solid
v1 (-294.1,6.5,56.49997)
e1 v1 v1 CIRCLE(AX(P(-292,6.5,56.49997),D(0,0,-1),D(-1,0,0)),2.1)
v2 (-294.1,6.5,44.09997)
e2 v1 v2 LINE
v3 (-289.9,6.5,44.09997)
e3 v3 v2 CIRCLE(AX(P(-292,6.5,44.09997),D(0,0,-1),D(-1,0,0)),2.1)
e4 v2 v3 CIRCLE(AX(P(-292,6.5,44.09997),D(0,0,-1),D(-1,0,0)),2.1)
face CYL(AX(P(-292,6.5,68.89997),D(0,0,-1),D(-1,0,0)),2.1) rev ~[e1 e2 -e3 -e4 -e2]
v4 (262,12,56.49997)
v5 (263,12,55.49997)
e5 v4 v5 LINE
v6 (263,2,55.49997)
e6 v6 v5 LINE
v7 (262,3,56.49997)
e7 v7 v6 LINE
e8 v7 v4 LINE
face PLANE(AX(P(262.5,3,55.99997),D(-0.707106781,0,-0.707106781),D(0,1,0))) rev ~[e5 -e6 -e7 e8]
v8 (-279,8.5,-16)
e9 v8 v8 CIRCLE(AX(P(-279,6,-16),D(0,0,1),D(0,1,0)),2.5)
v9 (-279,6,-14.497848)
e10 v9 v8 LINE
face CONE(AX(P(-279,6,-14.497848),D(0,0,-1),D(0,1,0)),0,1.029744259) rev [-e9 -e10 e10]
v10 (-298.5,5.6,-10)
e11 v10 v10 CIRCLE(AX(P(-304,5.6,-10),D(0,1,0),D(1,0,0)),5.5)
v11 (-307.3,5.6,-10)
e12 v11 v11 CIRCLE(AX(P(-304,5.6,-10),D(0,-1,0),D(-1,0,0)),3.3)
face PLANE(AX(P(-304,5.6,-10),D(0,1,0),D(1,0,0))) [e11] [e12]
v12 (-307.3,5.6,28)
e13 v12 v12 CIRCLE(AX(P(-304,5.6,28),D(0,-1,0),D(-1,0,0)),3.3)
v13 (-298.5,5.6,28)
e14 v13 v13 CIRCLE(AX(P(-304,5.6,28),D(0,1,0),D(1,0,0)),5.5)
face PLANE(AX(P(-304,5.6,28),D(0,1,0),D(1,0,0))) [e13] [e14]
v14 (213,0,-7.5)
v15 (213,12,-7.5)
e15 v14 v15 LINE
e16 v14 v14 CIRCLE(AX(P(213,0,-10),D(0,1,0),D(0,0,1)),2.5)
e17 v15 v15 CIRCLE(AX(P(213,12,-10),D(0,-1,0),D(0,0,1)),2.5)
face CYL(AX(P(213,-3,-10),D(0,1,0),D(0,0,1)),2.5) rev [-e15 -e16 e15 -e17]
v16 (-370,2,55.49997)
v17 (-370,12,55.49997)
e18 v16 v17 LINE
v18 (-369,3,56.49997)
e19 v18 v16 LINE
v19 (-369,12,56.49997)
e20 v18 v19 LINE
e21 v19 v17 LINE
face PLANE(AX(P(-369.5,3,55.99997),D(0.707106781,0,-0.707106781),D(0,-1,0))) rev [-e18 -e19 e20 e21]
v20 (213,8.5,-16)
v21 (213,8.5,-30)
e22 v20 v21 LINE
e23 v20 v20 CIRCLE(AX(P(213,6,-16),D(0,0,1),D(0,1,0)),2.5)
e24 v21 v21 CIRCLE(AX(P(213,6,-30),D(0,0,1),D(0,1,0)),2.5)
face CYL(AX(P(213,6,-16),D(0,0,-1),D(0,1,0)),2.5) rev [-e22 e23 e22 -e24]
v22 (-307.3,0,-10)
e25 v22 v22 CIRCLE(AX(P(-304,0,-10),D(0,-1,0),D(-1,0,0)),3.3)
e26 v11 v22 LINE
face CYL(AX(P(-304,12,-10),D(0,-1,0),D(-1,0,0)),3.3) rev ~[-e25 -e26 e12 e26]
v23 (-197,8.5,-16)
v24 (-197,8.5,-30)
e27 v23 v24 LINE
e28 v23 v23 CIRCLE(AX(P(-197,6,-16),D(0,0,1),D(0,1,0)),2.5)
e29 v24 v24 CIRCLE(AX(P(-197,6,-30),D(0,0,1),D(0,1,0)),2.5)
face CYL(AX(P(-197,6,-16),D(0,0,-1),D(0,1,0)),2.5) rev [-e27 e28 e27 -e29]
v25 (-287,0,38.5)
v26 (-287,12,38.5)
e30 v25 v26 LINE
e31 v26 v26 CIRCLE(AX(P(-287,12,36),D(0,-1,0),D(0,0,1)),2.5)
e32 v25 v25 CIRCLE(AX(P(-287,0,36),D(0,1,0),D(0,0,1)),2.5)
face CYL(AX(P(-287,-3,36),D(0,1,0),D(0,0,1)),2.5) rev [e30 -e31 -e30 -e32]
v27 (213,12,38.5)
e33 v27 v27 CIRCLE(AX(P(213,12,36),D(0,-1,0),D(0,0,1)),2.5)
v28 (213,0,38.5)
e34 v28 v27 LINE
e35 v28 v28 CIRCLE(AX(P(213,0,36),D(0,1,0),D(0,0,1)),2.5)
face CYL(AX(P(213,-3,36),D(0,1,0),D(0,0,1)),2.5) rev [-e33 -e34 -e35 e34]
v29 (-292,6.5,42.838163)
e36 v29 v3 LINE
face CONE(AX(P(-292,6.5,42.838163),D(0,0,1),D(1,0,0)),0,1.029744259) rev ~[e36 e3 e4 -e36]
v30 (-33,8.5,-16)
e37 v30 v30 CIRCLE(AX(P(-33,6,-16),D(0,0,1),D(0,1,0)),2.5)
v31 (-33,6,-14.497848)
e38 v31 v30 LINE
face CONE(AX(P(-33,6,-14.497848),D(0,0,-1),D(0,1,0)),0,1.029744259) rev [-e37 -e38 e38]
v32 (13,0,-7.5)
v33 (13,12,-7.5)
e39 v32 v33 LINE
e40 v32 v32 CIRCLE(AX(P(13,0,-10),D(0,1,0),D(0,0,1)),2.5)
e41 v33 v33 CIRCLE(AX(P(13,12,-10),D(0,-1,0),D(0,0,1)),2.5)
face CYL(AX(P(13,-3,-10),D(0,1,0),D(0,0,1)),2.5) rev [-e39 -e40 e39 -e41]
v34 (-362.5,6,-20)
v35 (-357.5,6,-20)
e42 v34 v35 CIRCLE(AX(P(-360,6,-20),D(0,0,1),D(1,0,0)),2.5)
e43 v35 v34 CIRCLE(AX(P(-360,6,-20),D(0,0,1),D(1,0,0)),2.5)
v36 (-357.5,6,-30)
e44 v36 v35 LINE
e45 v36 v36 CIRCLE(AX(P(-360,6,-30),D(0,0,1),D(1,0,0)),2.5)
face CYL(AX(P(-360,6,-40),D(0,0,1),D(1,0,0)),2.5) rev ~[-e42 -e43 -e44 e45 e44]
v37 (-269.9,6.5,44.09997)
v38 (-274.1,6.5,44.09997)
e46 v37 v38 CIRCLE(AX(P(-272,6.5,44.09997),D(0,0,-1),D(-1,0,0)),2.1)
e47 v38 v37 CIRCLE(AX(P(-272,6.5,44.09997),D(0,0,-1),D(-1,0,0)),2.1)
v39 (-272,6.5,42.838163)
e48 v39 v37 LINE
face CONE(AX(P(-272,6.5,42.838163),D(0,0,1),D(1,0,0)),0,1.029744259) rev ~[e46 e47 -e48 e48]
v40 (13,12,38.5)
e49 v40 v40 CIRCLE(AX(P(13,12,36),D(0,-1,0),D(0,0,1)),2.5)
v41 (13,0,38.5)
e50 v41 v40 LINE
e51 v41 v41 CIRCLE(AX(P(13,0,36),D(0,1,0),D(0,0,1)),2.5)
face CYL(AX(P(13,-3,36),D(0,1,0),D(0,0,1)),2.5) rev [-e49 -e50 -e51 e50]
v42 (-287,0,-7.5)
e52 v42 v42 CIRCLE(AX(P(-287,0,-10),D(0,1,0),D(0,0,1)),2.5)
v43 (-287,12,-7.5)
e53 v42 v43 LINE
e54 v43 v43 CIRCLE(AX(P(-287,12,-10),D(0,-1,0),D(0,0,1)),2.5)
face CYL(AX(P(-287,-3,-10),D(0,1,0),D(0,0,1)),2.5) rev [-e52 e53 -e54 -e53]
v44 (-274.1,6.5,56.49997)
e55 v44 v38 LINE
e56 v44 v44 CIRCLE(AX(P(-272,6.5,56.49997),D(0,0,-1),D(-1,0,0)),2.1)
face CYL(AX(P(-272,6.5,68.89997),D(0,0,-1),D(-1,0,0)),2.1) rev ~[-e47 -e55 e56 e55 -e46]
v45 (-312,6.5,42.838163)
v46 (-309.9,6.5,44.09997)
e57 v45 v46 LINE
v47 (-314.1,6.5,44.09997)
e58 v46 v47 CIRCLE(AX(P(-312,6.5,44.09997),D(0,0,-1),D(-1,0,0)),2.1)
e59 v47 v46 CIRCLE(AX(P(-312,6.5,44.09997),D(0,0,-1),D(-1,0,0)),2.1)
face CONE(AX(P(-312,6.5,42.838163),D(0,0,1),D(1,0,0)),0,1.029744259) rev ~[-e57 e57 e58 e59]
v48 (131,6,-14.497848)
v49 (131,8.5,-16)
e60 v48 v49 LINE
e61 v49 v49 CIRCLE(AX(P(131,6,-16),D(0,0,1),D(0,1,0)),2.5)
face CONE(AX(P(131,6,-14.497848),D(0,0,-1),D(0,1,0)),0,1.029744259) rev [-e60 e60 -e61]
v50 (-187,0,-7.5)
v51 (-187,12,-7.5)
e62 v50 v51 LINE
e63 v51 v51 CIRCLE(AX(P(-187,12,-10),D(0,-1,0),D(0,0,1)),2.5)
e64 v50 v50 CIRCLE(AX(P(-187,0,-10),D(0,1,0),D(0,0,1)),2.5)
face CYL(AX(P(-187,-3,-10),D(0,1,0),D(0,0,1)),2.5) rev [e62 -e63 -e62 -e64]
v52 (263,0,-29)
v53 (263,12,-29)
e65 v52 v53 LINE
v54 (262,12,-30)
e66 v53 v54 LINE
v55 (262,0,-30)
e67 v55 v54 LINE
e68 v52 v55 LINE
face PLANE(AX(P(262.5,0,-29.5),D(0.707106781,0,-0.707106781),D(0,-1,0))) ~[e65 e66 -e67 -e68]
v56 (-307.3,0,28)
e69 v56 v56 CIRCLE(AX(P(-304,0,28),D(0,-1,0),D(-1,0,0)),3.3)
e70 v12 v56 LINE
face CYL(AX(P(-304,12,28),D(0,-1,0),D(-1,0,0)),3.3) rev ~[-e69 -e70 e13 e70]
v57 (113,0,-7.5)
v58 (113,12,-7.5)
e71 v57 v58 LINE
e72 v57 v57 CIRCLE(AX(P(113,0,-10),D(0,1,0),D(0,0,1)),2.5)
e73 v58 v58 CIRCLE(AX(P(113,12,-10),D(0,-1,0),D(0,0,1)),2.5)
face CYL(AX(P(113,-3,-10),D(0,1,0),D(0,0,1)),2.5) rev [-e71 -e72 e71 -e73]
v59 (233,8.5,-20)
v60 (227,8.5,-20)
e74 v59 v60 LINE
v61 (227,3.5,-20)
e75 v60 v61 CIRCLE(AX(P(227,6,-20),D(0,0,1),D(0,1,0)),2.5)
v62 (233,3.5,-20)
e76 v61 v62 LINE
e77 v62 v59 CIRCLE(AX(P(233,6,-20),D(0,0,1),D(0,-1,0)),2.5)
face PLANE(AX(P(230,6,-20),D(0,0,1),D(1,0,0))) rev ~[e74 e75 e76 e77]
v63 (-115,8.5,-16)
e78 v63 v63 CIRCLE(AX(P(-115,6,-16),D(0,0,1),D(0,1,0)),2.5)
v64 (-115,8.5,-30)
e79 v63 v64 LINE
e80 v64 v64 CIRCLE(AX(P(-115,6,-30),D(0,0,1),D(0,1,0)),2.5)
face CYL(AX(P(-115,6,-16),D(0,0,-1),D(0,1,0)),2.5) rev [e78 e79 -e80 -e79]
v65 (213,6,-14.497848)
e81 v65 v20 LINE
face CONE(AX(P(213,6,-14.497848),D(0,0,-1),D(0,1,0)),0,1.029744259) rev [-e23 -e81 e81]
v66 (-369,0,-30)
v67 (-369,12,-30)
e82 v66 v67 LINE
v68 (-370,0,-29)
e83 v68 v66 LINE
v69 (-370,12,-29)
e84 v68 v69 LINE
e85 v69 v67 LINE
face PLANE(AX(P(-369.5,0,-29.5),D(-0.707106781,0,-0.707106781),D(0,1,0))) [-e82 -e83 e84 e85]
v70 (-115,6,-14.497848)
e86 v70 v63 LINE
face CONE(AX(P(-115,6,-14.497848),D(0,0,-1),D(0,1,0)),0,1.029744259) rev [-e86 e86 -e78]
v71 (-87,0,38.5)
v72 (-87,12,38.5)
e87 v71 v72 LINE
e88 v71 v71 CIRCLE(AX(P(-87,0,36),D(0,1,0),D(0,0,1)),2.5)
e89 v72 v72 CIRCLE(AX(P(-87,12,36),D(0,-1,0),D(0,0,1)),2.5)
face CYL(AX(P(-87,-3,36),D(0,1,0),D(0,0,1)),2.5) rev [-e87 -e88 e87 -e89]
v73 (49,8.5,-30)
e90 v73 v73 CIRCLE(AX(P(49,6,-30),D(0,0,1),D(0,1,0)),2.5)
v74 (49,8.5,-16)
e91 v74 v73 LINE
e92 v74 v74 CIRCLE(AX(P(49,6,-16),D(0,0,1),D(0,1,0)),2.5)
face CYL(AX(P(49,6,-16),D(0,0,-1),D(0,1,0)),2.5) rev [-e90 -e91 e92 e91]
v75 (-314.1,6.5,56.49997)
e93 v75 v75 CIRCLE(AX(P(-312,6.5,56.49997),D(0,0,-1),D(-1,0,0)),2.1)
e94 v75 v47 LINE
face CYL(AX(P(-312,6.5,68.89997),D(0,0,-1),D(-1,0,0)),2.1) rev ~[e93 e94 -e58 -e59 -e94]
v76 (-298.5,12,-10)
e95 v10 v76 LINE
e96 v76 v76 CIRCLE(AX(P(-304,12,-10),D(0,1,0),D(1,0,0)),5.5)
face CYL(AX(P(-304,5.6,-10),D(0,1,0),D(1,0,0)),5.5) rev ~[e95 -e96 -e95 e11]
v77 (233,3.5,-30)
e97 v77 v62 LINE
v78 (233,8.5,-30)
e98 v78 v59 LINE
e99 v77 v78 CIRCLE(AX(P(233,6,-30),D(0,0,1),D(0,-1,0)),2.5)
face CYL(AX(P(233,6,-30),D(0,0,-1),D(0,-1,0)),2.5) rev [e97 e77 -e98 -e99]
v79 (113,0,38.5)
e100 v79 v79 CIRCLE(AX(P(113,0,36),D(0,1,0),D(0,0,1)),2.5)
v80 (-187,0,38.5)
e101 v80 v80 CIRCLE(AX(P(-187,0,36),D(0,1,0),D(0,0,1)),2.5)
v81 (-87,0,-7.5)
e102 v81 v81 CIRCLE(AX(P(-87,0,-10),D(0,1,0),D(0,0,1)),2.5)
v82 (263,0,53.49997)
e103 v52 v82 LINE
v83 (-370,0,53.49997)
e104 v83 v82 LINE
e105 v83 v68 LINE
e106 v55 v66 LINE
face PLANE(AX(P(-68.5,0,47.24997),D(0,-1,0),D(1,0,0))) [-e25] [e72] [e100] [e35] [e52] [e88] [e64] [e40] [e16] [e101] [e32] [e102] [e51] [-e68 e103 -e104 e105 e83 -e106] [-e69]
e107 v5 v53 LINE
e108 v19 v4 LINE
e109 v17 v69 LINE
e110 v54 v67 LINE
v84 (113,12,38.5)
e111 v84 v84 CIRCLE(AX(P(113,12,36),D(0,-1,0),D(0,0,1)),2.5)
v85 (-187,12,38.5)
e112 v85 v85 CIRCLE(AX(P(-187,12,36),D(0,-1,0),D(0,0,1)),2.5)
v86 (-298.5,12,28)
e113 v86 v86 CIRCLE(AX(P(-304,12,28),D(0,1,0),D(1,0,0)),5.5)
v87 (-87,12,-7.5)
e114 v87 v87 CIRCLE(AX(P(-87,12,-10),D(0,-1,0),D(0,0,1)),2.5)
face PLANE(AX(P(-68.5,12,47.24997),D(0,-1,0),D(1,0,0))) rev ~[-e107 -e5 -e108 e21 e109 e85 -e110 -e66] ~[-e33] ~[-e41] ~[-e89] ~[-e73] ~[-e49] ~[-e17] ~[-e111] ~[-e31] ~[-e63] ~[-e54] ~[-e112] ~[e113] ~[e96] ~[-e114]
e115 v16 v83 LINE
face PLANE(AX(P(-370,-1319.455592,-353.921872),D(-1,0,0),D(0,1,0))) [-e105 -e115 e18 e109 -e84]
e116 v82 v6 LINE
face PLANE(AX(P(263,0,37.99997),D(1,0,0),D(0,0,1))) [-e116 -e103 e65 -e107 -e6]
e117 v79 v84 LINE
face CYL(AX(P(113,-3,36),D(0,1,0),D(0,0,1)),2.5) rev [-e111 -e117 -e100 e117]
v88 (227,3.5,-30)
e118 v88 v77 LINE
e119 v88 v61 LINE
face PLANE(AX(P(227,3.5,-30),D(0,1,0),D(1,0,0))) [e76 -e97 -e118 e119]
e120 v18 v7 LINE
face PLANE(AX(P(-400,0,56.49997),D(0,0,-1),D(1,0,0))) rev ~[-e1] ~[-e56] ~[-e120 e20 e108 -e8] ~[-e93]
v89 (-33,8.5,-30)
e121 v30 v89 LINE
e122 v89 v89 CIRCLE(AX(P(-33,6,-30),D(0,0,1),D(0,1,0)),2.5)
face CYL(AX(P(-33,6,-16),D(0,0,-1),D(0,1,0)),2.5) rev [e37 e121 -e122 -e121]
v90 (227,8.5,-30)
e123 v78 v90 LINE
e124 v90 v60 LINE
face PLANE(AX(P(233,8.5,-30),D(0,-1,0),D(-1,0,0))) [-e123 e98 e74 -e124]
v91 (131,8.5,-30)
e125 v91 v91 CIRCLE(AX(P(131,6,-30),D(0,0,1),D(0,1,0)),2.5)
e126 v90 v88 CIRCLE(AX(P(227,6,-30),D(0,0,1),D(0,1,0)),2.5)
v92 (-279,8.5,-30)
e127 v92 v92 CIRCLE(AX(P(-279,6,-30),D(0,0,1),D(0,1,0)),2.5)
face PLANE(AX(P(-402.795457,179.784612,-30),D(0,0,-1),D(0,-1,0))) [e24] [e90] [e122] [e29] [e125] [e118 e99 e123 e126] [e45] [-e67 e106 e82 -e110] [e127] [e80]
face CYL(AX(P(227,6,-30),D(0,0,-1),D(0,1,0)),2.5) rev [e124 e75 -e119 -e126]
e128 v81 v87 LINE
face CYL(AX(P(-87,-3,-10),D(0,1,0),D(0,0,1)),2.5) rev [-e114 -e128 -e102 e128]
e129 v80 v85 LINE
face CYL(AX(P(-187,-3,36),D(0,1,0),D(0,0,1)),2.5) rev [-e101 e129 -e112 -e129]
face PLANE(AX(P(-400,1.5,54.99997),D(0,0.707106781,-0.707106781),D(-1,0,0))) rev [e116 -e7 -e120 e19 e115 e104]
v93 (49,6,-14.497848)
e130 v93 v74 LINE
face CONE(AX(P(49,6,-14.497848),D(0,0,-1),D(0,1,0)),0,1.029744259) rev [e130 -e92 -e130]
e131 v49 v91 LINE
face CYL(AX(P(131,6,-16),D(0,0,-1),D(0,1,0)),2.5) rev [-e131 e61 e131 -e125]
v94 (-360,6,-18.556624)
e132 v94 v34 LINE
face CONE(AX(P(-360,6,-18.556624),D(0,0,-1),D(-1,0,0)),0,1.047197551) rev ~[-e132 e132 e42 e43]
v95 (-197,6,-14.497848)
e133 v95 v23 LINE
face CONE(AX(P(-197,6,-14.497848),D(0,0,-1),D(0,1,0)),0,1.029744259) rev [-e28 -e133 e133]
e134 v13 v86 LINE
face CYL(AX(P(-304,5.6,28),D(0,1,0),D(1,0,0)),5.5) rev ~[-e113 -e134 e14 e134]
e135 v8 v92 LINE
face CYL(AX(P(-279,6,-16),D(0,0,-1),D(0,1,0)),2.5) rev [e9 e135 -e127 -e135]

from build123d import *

# Parameters (mm, degrees)
SKETCH_1_W                     = 800
SKETCH_1_H                     = 80
EXTRUDE_1_DEPTH                = 12
SKETCH_13_W                    = 10
SKETCH_13_H                    = 40
EXTRUDE_2_DEPTH                = 800
CUT_EXTRUDE_1_DEPTH            = 409.881400898
CUT_EXTRUDE_1_DEPTH_BACK       = 409.881400898
SKETCH_15_W                    = 47
SKETCH_15_H                    = 70
CUT_EXTRUDE_2_DEPTH            = 403.968981437
CUT_EXTRUDE_3_DEPTH            = 665.795457265
CUT_EXTRUDE_3_DEPTH_BACK       = 665.795457265
CUT_EXTRUDE_4_DEPTH            = 665.795457265
CUT_EXTRUDE_4_DEPTH_BACK       = 665.795457265
PATTERN_LINEAR_1_COUNT         = 7
PATTERN_LINEAR_1_PITCH         = 82
HOLE_WIZARD_M6_1_2_D           = 6.6
HOLE_WIZARD_M6_1_2_CBORE_D     = 11
HOLE_WIZARD_M6_1_2_CBORE_DEPTH = 6.4
HOLE_WIZARD_5_0_5_1_D          = 5
HOLE_WIZARD_5_0_5_1_DEPTH      = 10
HOLE_WIZARD_5_0_5_1_TIP        = 1.443375673
CUT_EXTRUDE_5_DEPTH            = 10
SKETCH_26_W                    = 663
SKETCH_26_H                    = 18.5
EXTRUDE_3_DEPTH                = 12
CHAMFER_1_SIZE                 = 3
HOLE_WIZARD_M6_2_AT_2_COUNT    = 2
HOLE_WIZARD_M6_2_AT_2_PITCH    = 46
PATTERN_LINEAR_2_COUNT         = 6
PATTERN_LINEAR_2_PITCH         = 100
HOLE_WIZARD_M5_1_D             = 4.2
HOLE_WIZARD_M5_1_DEPTH         = 12.4
HOLE_WIZARD_M5_1_TIP           = 1.2618073
CUT_EXTRUDE_6_DEPTH            = 410.421842126
CUT_EXTRUDE_6_DEPTH_BACK       = 410.421842126
CHAMFER_2_SIZE                 = 1


with BuildPart() as part:
    # 草图1 → 凸台-拉伸1 (new body)
    with BuildSketch(Plane(origin=(0, 0, 0), x_dir=(1, 0, 0), z_dir=(0, 1, 0))):
        Rectangle(SKETCH_1_W, SKETCH_1_H)
    extrude(amount=EXTRUDE_1_DEPTH)

    # 草图13 → 凸台-拉伸2 (add)
    with BuildSketch(Plane(origin=(400, 0, 0), x_dir=(0, 0, -1), z_dir=(1, 0, 0))):
        with Locations((35, -8)):
            Rectangle(SKETCH_13_W, SKETCH_13_H)
    extrude(amount=-EXTRUDE_2_DEPTH)

    # 草图14 → 切除-拉伸1 (cut, two sides: drawn at the far end of the back side and taken through both)
    with BuildSketch(Plane.XY.offset(40).offset(-CUT_EXTRUDE_1_DEPTH_BACK)):
        Polygon((310, 1445.673153531), (310, 12), (310, -39.100998243), (310, -1472.774151774), (3177.346307063, -1472.774151774), (3177.346307063, 1445.673153531), align=None)
    extrude(amount=CUT_EXTRUDE_1_DEPTH + CUT_EXTRUDE_1_DEPTH_BACK, mode=Mode.SUBTRACT)

    # 草图15 → 切除-拉伸2 (cut, through all)
    with BuildSketch(Plane.XZ):
        with Locations((286.5, 5)):
            Rectangle(SKETCH_15_W, SKETCH_15_H)
    extrude(amount=-CUT_EXTRUDE_2_DEPTH, mode=Mode.SUBTRACT)

    # 草图16 → 切除-拉伸3 (cut, two sides: drawn at the far end of the back side and taken through both)
    with BuildSketch(Plane(origin=(263, 0, 0), x_dir=(0, 0, -1), z_dir=(1, 0, 0)).offset(-CUT_EXTRUDE_3_DEPTH_BACK)):
        Polygon((-37.99997, 201.49334526), (-37.99997, 14.161837787), (-37.99997, -5.873299283), (-37.99997, -193.204806756), (-412.662984945, -193.204806756), (-412.662984945, 201.49334526), align=None)
    extrude(amount=CUT_EXTRUDE_3_DEPTH + CUT_EXTRUDE_3_DEPTH_BACK, mode=Mode.SUBTRACT)

    # 草图17 → 切除-拉伸4 (cut, two sides: drawn at the far end of the back side and taken through both)
    with BuildSketch(Plane(origin=(263, 0, 0), x_dir=(0, 0, -1), z_dir=(1, 0, 0)).offset(-CUT_EXTRUDE_4_DEPTH_BACK)):
        Polygon((30, 179.784611671), (30, 12), (30, -28), (30, -195.784611671), (365.569223341, -195.784611671), (365.569223341, 179.784611671), align=None)
    extrude(amount=CUT_EXTRUDE_4_DEPTH + CUT_EXTRUDE_4_DEPTH_BACK, mode=Mode.SUBTRACT)

    # 草图18 → Hole Wizard M6 _1 (revolve, cut)
    with BuildSketch(Plane(origin=(213, 6, -30), x_dir=(0, 1, 0), z_dir=(1, 0, 0))):
        Polygon((0, 0), (0, 15.502151548), (2.5, 14), (2.5, 0), align=None)
    hole_wizard_m6_1 = revolve(axis=Axis((213, 6, -36.35), (0, 0, 1)), mode=Mode.SUBTRACT)

    # 阵列(线性)1: Hole Wizard M6 _1 ×7
    with Locations(*[(-i * PATTERN_LINEAR_1_PITCH, 0, 0) for i in range(1, PATTERN_LINEAR_1_COUNT)]):
        add(hole_wizard_m6_1, mode=Mode.SUBTRACT)

    # Hole Wizard M6 _1 2 (through all)
    with Locations(Plane(origin=(0, 12, 0), x_dir=(1, 0, 0), z_dir=(0, 1, 0))):
        with Locations((-304, 10), (-304, -28)):
            CounterBoreHole(HOLE_WIZARD_M6_1_2_D / 2, HOLE_WIZARD_M6_1_2_CBORE_D / 2, HOLE_WIZARD_M6_1_2_CBORE_DEPTH)

    # Ø5.0 (5) 直径孔1
    with Locations(Plane(origin=(0, 0, -30), x_dir=(-1, 0, 0), z_dir=(0, 0, -1))):
        with Locations((360, 6)):
            Hole(HOLE_WIZARD_5_0_5_1_D / 2, depth=HOLE_WIZARD_5_0_5_1_DEPTH)
            with Locations((0, 0, -(HOLE_WIZARD_5_0_5_1_DEPTH + HOLE_WIZARD_5_0_5_1_TIP / 2))):  # 120° drill point
                Cone(0, HOLE_WIZARD_5_0_5_1_D / 2, HOLE_WIZARD_5_0_5_1_TIP, mode=Mode.SUBTRACT)

    # 草图24 → 切除-拉伸5 (cut)
    with BuildSketch(Plane(origin=(0, 0, -30), x_dir=(-1, 0, 0), z_dir=(0, 0, -1))):
        with BuildLine():
            Line((-227, 3.5), (-233, 3.5))
            ThreePointArc((-233, 3.5), (-235.5, 6), (-233, 8.5))
            Line((-233, 8.5), (-227, 8.5))
            ThreePointArc((-227, 8.5), (-224.5, 6), (-227, 3.5))
        make_face()
    extrude(amount=-CUT_EXTRUDE_5_DEPTH, mode=Mode.SUBTRACT)

    # 草图26 → 凸台-拉伸3 (add)
    with BuildSketch(Plane.XZ):
        with Locations((-68.5, 47.24997)):
            Rectangle(SKETCH_26_W, SKETCH_26_H)
    extrude(amount=-EXTRUDE_3_DEPTH)

    # 倒角1
    chamfer_1_edges = [part.edges().sort_by_distance(p)[0] for p in [
        (-68.5, 0, 56.49997),
    ]]
    chamfer(chamfer_1_edges, length=CHAMFER_1_SIZE)

    # 草图27 → M6 螺纹孔2 (revolve, cut)
    with BuildSketch(Plane(origin=(213, 12, -10), x_dir=(0, 0, 1), z_dir=(1, 0, 0))):
        Polygon((0, 0), (0, 16.502151548), (2.5, 15), (2.5, 0), align=None)
    hole_wizard_m6_2 = revolve(axis=Axis((213, 18.35, -10), (0, -1, 0)), mode=Mode.SUBTRACT)

    # M6 螺纹孔2 at 2: M6 螺纹孔2 ×2
    with Locations(*[(0, 0, i * HOLE_WIZARD_M6_2_AT_2_PITCH) for i in range(1, HOLE_WIZARD_M6_2_AT_2_COUNT)]):
        add(hole_wizard_m6_2, mode=Mode.SUBTRACT)

    # 阵列(线性)2: M6 螺纹孔2 ×6
    with Locations(*[(-i * PATTERN_LINEAR_2_PITCH, 0, 0) for i in range(1, PATTERN_LINEAR_2_COUNT)]):
        add(hole_wizard_m6_2, mode=Mode.SUBTRACT)

    # 阵列(线性)2 copy 1 sketch → 阵列(线性)2 copy 1 (revolve, cut)
    with BuildSketch(Plane(origin=(113, 12, 36), x_dir=(0, 0, 1), z_dir=(1, 0, 0))):
        Polygon((0, 0), (0, 16.502151548), (2.5, 15), (2.5, 0), align=None)
    revolve(axis=Axis((113, 18.35, 36), (0, -1, 0)), mode=Mode.SUBTRACT)

    # 阵列(线性)2 copy 2 sketch → 阵列(线性)2 copy 2 (revolve, cut)
    with BuildSketch(Plane(origin=(13, 12, 36), x_dir=(0, 0, 1), z_dir=(1, 0, 0))):
        Polygon((0, 0), (0, 16.502151548), (2.5, 15), (2.5, 0), align=None)
    revolve(axis=Axis((13, 18.35, 36), (0, -1, 0)), mode=Mode.SUBTRACT)

    # 阵列(线性)2 copy 3 sketch → 阵列(线性)2 copy 3 (revolve, cut)
    with BuildSketch(Plane(origin=(-87, 12, 36), x_dir=(0, 0, 1), z_dir=(1, 0, 0))):
        Polygon((0, 0), (0, 16.502151548), (2.5, 15), (2.5, 0), align=None)
    revolve(axis=Axis((-87, 18.35, 36), (0, -1, 0)), mode=Mode.SUBTRACT)

    # 阵列(线性)2 copy 4 sketch → 阵列(线性)2 copy 4 (revolve, cut)
    with BuildSketch(Plane(origin=(-187, 12, 36), x_dir=(0, 0, 1), z_dir=(1, 0, 0))):
        Polygon((0, 0), (0, 16.502151548), (2.5, 15), (2.5, 0), align=None)
    revolve(axis=Axis((-187, 18.35, 36), (0, -1, 0)), mode=Mode.SUBTRACT)

    # 阵列(线性)2 copy 5 sketch → 阵列(线性)2 copy 5 (revolve, cut)
    with BuildSketch(Plane(origin=(-287, 12, 36), x_dir=(0, 0, 1), z_dir=(1, 0, 0))):
        Polygon((0, 0), (0, 16.502151548), (2.5, 15), (2.5, 0), align=None)
    revolve(axis=Axis((-287, 18.35, 36), (0, -1, 0)), mode=Mode.SUBTRACT)

    # M5 螺纹孔1
    with Locations(Plane.XY.offset(56.49997)):
        with Locations((-312.000000001, 6.5), (-292.000000001, 6.5), (-272.000000001, 6.5)):
            Hole(HOLE_WIZARD_M5_1_D / 2, depth=HOLE_WIZARD_M5_1_DEPTH)
            with Locations((0, 0, -(HOLE_WIZARD_M5_1_DEPTH + HOLE_WIZARD_M5_1_TIP / 2))):  # 118° drill point
                Cone(0, HOLE_WIZARD_M5_1_D / 2, HOLE_WIZARD_M5_1_TIP, mode=Mode.SUBTRACT)

    # 草图31 → 切除-拉伸6 (cut, two sides: drawn at the far end of the back side and taken through both)
    with BuildSketch(Plane.XY.offset(56.49997).offset(-CUT_EXTRUDE_6_DEPTH_BACK)):
        Polygon((-370, 1306.901366583), (-370, 26.75), (-370, -39.304225055), (-370, -1319.455591638), (-2930.302733167, -1319.455591638), (-2930.302733167, 1306.901366583), align=None)
    extrude(amount=CUT_EXTRUDE_6_DEPTH + CUT_EXTRUDE_6_DEPTH_BACK, mode=Mode.SUBTRACT)

    # 倒角2
    chamfer_2_edges = [part.edges().sort_by_distance(p)[0] for p in [
        (263, 7.5, 56.49997),
        (-370, 6, -30),
        (-370, 7.5, 56.49997),
        (263, 6, -30),
    ]]
    chamfer(chamfer_2_edges, length=CHAMFER_2_SIZE)


solid = part.part
